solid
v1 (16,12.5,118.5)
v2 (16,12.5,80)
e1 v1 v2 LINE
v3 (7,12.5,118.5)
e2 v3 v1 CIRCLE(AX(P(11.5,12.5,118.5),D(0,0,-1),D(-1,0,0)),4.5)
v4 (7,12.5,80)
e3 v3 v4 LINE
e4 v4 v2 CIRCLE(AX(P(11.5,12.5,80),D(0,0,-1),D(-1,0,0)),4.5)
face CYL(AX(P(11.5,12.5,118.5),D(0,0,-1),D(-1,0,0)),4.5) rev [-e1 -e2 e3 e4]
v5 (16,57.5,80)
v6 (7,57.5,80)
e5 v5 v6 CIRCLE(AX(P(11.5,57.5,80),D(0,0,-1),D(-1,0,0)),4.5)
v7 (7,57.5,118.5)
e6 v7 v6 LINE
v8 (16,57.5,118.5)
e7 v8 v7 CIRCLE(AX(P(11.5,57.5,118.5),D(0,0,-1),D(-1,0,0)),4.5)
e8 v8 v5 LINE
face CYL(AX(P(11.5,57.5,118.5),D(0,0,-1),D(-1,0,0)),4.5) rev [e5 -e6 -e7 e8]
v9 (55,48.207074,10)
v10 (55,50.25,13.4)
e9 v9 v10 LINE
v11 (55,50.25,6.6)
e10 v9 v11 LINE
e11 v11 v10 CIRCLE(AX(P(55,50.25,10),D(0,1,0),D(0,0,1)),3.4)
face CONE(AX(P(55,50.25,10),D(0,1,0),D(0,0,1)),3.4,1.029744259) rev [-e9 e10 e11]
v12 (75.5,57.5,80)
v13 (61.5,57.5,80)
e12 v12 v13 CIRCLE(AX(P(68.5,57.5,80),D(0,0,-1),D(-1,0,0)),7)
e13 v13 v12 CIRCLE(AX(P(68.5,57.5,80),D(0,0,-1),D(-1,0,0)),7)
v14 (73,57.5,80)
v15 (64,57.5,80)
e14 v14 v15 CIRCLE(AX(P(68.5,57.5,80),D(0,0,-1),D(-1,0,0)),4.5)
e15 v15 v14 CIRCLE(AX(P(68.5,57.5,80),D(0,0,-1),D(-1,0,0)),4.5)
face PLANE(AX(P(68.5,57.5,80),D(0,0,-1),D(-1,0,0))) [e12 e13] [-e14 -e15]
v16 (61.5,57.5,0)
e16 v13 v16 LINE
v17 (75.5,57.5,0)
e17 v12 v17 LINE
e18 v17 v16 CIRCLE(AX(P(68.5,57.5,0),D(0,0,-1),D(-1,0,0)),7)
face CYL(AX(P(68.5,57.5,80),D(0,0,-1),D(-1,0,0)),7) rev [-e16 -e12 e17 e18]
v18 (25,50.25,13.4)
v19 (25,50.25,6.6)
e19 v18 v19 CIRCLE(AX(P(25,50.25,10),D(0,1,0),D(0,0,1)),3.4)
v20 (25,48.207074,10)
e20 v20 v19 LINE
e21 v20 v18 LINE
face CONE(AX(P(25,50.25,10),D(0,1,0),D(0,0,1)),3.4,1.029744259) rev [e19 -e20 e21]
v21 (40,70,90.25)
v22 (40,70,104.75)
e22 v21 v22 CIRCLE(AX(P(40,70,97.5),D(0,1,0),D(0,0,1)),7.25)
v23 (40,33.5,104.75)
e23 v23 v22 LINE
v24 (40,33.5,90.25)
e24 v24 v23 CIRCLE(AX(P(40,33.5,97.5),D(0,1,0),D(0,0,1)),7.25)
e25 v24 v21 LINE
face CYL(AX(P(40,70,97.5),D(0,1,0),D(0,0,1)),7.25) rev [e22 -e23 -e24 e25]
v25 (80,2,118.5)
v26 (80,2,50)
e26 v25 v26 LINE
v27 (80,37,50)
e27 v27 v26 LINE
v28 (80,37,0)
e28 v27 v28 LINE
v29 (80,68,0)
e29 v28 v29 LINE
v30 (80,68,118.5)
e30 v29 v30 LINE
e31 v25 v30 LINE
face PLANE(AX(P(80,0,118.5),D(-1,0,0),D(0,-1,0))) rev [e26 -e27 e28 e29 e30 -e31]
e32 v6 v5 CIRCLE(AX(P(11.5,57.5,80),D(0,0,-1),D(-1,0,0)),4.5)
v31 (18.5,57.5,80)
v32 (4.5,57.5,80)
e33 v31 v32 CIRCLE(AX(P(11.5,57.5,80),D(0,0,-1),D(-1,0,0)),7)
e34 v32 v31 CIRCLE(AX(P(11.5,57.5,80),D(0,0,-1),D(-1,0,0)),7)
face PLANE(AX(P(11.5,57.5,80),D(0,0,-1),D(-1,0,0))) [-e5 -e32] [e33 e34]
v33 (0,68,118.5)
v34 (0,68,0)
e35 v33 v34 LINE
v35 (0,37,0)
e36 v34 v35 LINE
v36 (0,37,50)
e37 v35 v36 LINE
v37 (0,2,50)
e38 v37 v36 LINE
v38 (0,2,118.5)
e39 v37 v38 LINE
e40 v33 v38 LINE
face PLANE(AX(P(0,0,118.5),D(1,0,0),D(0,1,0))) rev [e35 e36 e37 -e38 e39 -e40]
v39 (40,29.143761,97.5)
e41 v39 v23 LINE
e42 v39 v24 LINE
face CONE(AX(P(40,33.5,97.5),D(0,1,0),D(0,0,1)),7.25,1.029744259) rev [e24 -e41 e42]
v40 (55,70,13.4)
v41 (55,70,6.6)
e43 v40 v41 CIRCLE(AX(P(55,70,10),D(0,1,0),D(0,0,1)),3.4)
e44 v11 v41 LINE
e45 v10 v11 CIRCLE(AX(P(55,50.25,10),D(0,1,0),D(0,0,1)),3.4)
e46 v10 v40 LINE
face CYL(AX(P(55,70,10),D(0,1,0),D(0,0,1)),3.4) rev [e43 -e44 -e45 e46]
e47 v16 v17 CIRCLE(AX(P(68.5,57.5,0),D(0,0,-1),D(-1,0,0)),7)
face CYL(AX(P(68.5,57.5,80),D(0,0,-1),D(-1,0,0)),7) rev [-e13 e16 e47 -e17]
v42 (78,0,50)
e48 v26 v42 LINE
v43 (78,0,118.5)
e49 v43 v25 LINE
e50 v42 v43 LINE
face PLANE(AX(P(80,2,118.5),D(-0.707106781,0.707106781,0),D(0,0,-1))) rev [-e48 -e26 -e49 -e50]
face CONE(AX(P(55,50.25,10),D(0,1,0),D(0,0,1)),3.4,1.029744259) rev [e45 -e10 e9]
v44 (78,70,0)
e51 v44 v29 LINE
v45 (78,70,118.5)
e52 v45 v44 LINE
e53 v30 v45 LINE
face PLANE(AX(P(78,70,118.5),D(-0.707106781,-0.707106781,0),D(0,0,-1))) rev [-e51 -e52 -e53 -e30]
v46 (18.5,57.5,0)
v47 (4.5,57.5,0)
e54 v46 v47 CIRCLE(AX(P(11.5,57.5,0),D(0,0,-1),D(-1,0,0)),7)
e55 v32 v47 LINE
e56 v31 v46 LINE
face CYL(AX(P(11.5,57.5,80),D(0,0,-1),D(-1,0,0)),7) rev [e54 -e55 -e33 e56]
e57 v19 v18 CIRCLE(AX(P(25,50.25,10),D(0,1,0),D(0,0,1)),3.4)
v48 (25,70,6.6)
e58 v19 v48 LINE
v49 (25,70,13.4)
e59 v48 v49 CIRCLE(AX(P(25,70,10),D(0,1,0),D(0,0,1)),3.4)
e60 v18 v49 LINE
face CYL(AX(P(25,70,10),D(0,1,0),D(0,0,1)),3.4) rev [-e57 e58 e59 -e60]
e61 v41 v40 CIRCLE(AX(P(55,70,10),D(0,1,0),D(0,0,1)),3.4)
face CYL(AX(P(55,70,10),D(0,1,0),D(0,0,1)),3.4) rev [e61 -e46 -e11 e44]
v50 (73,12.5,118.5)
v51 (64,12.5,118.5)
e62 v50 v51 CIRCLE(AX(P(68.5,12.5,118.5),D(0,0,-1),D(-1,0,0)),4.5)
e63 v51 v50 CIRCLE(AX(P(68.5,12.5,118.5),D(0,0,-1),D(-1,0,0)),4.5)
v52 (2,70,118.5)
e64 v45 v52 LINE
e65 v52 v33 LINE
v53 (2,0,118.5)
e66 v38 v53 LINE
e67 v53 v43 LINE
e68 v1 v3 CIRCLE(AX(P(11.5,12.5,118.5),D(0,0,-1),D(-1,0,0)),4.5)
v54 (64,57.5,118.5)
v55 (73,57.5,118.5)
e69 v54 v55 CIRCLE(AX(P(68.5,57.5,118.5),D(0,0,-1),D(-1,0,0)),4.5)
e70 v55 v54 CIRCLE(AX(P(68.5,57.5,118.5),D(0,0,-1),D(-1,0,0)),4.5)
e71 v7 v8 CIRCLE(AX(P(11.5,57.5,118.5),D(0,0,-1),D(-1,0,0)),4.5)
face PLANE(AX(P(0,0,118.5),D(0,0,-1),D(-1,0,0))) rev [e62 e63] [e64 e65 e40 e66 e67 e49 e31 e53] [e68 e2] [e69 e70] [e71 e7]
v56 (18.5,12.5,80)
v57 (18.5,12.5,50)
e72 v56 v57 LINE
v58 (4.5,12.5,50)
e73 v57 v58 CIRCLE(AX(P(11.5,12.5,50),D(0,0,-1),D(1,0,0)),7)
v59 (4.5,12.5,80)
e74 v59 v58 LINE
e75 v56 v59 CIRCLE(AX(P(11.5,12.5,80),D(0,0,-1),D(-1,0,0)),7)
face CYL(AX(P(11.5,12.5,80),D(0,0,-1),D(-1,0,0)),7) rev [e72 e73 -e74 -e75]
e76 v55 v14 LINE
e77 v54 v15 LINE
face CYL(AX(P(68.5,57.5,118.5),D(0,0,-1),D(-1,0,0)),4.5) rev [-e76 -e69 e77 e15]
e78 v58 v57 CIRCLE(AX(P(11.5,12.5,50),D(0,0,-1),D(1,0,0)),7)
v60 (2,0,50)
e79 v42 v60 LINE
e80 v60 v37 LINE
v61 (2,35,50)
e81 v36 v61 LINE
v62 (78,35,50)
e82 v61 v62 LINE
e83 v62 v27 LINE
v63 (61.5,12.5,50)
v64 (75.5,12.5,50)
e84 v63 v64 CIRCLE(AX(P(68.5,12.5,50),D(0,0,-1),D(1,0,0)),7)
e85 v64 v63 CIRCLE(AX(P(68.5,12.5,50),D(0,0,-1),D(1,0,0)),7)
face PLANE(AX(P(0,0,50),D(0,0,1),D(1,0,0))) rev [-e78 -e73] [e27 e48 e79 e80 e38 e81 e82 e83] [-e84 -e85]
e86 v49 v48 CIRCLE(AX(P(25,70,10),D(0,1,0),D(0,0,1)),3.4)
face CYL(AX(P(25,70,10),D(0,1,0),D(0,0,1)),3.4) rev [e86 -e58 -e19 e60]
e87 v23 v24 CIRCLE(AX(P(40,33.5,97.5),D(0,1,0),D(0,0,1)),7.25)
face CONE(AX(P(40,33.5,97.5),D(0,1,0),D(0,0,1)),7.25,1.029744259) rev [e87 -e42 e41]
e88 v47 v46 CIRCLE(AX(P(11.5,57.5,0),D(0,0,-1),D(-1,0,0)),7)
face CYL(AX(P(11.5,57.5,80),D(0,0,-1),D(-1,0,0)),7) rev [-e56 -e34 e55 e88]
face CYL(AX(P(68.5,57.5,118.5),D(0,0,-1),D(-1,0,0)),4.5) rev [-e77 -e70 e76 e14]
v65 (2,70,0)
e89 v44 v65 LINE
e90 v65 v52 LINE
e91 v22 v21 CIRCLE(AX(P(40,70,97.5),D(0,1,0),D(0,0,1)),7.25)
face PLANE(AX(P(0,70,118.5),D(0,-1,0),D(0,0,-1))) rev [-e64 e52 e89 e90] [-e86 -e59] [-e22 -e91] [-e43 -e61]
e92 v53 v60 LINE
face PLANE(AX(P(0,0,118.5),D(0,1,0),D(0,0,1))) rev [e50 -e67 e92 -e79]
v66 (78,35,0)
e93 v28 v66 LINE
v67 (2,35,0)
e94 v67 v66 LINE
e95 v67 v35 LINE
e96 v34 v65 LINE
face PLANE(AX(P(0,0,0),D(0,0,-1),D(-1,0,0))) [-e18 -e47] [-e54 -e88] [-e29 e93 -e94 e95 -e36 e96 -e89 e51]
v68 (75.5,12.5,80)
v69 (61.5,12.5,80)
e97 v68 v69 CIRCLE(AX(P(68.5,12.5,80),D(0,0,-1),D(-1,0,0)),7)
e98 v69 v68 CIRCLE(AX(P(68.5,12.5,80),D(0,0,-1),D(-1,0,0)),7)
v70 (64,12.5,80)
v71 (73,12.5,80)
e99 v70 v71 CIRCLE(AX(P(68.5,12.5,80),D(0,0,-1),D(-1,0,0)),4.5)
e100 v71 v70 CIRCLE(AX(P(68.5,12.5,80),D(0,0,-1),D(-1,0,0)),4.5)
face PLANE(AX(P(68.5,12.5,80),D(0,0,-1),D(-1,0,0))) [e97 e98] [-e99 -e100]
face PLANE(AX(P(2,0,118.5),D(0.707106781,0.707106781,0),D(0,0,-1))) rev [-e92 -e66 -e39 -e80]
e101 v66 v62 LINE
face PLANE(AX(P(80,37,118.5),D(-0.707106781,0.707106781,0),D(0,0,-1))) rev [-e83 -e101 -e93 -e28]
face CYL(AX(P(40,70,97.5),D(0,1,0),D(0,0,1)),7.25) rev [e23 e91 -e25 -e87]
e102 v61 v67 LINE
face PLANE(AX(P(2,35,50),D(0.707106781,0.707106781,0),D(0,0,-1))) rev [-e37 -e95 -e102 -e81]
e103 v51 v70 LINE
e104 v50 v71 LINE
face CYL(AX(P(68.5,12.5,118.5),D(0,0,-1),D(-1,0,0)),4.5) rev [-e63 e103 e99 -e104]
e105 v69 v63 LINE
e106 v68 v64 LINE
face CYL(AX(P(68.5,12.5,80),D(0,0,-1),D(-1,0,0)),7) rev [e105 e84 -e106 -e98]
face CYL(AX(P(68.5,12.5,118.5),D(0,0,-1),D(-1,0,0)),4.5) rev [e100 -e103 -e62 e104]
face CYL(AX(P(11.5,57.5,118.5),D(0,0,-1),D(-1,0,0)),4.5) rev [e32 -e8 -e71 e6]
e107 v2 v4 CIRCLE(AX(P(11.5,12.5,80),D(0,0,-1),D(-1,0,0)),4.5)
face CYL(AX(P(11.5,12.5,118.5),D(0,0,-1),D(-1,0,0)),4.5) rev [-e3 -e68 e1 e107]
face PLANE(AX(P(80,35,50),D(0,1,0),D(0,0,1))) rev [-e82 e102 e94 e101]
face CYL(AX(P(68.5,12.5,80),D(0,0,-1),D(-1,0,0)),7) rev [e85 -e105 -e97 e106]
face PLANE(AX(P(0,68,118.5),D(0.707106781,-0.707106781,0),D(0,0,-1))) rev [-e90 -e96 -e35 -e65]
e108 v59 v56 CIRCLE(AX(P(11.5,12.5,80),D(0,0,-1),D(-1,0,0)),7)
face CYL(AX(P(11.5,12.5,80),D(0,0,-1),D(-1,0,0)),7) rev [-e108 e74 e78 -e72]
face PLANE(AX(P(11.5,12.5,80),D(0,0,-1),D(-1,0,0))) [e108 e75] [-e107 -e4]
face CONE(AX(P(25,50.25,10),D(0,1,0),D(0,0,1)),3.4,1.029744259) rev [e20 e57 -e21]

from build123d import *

# Parameters (mm, degrees)
SKETCH_1_W             = 80
SKETCH_1_H             = 70
EXTRUDE_1_DEPTH        = 118.5
SKETCH_4_R             = 7
CUT_EXTRUDE_1_DEPTH    = 80
SKETCH_5_R             = 4.5
CUT_EXTRUDE_2_DEPTH    = 160.192493542
SKETCH_6_W             = 80
SKETCH_6_H             = 35
CUT_EXTRUDE_3_DEPTH    = 50
M16X1_5_1_D            = 14.5
M16X1_5_1_DEPTH        = 36.5
M16X1_5_1_TIP          = 4.356239488
HOLE_WIZARD_M8_1_D     = 6.8
HOLE_WIZARD_M8_1_DEPTH = 19.75
HOLE_WIZARD_M8_1_TIP   = 2.042926105
CHAMFER_1_SIZE         = 2


with BuildPart() as part:
    # 草图1 → 凸台-拉伸1 (new body)
    with BuildSketch(Plane.XY):
        with Locations((40, 35)):
            Rectangle(SKETCH_1_W, SKETCH_1_H)
    extrude(amount=EXTRUDE_1_DEPTH)

    # 草图4 → 切除-拉伸1 (cut)
    with BuildSketch(Plane(origin=(0, 0, 0), x_dir=(-1, 0, 0), z_dir=(0, 0, -1))):
        with Locations((-11.5, 57.5)):
            Circle(SKETCH_4_R)
        with Locations((-11.5, 12.5)):
            Circle(SKETCH_4_R)
        with Locations((-68.5, 57.5)):
            Circle(SKETCH_4_R)
        with Locations((-68.5, 12.5)):
            Circle(SKETCH_4_R)
    extrude(amount=-CUT_EXTRUDE_1_DEPTH, mode=Mode.SUBTRACT)

    # 草图5 → 切除-拉伸2 (cut, through all)
    with BuildSketch(Plane(origin=(0, 0, 0), x_dir=(-1, 0, 0), z_dir=(0, 0, -1))):
        with Locations((-68.5, 57.5)):
            Circle(SKETCH_5_R)
        with Locations((-11.5, 57.5)):
            Circle(SKETCH_5_R)
        with Locations((-11.5, 12.5)):
            Circle(SKETCH_5_R)
        with Locations((-68.5, 12.5)):
            Circle(SKETCH_5_R)
    extrude(amount=-CUT_EXTRUDE_2_DEPTH, mode=Mode.SUBTRACT)

    # 草图6 → 切除-拉伸3 (cut)
    with BuildSketch(Plane(origin=(0, 0, 0), x_dir=(-1, 0, 0), z_dir=(0, 0, -1))):
        with Locations((-40, 17.5)):
            Rectangle(SKETCH_6_W, SKETCH_6_H)
    extrude(amount=-CUT_EXTRUDE_3_DEPTH, mode=Mode.SUBTRACT)

    # M16x1.5 螺纹孔1
    with Locations(Plane(origin=(0, 70, 0), x_dir=(1, 0, 0), z_dir=(0, 1, 0))):
        with Locations((40, -97.5)):
            Hole(M16X1_5_1_D / 2, depth=M16X1_5_1_DEPTH)
            with Locations((0, 0, -(M16X1_5_1_DEPTH + M16X1_5_1_TIP / 2))):  # 118° drill point
                Cone(0, M16X1_5_1_D / 2, M16X1_5_1_TIP, mode=Mode.SUBTRACT)

    # M8 螺纹孔1
    with Locations(Plane(origin=(0, 70, 0), x_dir=(1, 0, 0), z_dir=(0, 1, 0))):
        with Locations((55, -10), (25, -10)):
            Hole(HOLE_WIZARD_M8_1_D / 2, depth=HOLE_WIZARD_M8_1_DEPTH)
            with Locations((0, 0, -(HOLE_WIZARD_M8_1_DEPTH + HOLE_WIZARD_M8_1_TIP / 2))):  # 118° drill point
                Cone(0, HOLE_WIZARD_M8_1_D / 2, HOLE_WIZARD_M8_1_TIP, mode=Mode.SUBTRACT)

    # 倒角1
    chamfer_1_edges = [part.edges().sort_by_distance(p)[0] for p in [
        (80, 35, 25),
        (0, 35, 25),
        (0, 70, 59.25),
        (80, 70, 59.25),
        (80, 0, 84.25),
        (0, 0, 84.25),
    ]]
    chamfer(chamfer_1_edges, length=CHAMFER_1_SIZE)


solid = part.part
